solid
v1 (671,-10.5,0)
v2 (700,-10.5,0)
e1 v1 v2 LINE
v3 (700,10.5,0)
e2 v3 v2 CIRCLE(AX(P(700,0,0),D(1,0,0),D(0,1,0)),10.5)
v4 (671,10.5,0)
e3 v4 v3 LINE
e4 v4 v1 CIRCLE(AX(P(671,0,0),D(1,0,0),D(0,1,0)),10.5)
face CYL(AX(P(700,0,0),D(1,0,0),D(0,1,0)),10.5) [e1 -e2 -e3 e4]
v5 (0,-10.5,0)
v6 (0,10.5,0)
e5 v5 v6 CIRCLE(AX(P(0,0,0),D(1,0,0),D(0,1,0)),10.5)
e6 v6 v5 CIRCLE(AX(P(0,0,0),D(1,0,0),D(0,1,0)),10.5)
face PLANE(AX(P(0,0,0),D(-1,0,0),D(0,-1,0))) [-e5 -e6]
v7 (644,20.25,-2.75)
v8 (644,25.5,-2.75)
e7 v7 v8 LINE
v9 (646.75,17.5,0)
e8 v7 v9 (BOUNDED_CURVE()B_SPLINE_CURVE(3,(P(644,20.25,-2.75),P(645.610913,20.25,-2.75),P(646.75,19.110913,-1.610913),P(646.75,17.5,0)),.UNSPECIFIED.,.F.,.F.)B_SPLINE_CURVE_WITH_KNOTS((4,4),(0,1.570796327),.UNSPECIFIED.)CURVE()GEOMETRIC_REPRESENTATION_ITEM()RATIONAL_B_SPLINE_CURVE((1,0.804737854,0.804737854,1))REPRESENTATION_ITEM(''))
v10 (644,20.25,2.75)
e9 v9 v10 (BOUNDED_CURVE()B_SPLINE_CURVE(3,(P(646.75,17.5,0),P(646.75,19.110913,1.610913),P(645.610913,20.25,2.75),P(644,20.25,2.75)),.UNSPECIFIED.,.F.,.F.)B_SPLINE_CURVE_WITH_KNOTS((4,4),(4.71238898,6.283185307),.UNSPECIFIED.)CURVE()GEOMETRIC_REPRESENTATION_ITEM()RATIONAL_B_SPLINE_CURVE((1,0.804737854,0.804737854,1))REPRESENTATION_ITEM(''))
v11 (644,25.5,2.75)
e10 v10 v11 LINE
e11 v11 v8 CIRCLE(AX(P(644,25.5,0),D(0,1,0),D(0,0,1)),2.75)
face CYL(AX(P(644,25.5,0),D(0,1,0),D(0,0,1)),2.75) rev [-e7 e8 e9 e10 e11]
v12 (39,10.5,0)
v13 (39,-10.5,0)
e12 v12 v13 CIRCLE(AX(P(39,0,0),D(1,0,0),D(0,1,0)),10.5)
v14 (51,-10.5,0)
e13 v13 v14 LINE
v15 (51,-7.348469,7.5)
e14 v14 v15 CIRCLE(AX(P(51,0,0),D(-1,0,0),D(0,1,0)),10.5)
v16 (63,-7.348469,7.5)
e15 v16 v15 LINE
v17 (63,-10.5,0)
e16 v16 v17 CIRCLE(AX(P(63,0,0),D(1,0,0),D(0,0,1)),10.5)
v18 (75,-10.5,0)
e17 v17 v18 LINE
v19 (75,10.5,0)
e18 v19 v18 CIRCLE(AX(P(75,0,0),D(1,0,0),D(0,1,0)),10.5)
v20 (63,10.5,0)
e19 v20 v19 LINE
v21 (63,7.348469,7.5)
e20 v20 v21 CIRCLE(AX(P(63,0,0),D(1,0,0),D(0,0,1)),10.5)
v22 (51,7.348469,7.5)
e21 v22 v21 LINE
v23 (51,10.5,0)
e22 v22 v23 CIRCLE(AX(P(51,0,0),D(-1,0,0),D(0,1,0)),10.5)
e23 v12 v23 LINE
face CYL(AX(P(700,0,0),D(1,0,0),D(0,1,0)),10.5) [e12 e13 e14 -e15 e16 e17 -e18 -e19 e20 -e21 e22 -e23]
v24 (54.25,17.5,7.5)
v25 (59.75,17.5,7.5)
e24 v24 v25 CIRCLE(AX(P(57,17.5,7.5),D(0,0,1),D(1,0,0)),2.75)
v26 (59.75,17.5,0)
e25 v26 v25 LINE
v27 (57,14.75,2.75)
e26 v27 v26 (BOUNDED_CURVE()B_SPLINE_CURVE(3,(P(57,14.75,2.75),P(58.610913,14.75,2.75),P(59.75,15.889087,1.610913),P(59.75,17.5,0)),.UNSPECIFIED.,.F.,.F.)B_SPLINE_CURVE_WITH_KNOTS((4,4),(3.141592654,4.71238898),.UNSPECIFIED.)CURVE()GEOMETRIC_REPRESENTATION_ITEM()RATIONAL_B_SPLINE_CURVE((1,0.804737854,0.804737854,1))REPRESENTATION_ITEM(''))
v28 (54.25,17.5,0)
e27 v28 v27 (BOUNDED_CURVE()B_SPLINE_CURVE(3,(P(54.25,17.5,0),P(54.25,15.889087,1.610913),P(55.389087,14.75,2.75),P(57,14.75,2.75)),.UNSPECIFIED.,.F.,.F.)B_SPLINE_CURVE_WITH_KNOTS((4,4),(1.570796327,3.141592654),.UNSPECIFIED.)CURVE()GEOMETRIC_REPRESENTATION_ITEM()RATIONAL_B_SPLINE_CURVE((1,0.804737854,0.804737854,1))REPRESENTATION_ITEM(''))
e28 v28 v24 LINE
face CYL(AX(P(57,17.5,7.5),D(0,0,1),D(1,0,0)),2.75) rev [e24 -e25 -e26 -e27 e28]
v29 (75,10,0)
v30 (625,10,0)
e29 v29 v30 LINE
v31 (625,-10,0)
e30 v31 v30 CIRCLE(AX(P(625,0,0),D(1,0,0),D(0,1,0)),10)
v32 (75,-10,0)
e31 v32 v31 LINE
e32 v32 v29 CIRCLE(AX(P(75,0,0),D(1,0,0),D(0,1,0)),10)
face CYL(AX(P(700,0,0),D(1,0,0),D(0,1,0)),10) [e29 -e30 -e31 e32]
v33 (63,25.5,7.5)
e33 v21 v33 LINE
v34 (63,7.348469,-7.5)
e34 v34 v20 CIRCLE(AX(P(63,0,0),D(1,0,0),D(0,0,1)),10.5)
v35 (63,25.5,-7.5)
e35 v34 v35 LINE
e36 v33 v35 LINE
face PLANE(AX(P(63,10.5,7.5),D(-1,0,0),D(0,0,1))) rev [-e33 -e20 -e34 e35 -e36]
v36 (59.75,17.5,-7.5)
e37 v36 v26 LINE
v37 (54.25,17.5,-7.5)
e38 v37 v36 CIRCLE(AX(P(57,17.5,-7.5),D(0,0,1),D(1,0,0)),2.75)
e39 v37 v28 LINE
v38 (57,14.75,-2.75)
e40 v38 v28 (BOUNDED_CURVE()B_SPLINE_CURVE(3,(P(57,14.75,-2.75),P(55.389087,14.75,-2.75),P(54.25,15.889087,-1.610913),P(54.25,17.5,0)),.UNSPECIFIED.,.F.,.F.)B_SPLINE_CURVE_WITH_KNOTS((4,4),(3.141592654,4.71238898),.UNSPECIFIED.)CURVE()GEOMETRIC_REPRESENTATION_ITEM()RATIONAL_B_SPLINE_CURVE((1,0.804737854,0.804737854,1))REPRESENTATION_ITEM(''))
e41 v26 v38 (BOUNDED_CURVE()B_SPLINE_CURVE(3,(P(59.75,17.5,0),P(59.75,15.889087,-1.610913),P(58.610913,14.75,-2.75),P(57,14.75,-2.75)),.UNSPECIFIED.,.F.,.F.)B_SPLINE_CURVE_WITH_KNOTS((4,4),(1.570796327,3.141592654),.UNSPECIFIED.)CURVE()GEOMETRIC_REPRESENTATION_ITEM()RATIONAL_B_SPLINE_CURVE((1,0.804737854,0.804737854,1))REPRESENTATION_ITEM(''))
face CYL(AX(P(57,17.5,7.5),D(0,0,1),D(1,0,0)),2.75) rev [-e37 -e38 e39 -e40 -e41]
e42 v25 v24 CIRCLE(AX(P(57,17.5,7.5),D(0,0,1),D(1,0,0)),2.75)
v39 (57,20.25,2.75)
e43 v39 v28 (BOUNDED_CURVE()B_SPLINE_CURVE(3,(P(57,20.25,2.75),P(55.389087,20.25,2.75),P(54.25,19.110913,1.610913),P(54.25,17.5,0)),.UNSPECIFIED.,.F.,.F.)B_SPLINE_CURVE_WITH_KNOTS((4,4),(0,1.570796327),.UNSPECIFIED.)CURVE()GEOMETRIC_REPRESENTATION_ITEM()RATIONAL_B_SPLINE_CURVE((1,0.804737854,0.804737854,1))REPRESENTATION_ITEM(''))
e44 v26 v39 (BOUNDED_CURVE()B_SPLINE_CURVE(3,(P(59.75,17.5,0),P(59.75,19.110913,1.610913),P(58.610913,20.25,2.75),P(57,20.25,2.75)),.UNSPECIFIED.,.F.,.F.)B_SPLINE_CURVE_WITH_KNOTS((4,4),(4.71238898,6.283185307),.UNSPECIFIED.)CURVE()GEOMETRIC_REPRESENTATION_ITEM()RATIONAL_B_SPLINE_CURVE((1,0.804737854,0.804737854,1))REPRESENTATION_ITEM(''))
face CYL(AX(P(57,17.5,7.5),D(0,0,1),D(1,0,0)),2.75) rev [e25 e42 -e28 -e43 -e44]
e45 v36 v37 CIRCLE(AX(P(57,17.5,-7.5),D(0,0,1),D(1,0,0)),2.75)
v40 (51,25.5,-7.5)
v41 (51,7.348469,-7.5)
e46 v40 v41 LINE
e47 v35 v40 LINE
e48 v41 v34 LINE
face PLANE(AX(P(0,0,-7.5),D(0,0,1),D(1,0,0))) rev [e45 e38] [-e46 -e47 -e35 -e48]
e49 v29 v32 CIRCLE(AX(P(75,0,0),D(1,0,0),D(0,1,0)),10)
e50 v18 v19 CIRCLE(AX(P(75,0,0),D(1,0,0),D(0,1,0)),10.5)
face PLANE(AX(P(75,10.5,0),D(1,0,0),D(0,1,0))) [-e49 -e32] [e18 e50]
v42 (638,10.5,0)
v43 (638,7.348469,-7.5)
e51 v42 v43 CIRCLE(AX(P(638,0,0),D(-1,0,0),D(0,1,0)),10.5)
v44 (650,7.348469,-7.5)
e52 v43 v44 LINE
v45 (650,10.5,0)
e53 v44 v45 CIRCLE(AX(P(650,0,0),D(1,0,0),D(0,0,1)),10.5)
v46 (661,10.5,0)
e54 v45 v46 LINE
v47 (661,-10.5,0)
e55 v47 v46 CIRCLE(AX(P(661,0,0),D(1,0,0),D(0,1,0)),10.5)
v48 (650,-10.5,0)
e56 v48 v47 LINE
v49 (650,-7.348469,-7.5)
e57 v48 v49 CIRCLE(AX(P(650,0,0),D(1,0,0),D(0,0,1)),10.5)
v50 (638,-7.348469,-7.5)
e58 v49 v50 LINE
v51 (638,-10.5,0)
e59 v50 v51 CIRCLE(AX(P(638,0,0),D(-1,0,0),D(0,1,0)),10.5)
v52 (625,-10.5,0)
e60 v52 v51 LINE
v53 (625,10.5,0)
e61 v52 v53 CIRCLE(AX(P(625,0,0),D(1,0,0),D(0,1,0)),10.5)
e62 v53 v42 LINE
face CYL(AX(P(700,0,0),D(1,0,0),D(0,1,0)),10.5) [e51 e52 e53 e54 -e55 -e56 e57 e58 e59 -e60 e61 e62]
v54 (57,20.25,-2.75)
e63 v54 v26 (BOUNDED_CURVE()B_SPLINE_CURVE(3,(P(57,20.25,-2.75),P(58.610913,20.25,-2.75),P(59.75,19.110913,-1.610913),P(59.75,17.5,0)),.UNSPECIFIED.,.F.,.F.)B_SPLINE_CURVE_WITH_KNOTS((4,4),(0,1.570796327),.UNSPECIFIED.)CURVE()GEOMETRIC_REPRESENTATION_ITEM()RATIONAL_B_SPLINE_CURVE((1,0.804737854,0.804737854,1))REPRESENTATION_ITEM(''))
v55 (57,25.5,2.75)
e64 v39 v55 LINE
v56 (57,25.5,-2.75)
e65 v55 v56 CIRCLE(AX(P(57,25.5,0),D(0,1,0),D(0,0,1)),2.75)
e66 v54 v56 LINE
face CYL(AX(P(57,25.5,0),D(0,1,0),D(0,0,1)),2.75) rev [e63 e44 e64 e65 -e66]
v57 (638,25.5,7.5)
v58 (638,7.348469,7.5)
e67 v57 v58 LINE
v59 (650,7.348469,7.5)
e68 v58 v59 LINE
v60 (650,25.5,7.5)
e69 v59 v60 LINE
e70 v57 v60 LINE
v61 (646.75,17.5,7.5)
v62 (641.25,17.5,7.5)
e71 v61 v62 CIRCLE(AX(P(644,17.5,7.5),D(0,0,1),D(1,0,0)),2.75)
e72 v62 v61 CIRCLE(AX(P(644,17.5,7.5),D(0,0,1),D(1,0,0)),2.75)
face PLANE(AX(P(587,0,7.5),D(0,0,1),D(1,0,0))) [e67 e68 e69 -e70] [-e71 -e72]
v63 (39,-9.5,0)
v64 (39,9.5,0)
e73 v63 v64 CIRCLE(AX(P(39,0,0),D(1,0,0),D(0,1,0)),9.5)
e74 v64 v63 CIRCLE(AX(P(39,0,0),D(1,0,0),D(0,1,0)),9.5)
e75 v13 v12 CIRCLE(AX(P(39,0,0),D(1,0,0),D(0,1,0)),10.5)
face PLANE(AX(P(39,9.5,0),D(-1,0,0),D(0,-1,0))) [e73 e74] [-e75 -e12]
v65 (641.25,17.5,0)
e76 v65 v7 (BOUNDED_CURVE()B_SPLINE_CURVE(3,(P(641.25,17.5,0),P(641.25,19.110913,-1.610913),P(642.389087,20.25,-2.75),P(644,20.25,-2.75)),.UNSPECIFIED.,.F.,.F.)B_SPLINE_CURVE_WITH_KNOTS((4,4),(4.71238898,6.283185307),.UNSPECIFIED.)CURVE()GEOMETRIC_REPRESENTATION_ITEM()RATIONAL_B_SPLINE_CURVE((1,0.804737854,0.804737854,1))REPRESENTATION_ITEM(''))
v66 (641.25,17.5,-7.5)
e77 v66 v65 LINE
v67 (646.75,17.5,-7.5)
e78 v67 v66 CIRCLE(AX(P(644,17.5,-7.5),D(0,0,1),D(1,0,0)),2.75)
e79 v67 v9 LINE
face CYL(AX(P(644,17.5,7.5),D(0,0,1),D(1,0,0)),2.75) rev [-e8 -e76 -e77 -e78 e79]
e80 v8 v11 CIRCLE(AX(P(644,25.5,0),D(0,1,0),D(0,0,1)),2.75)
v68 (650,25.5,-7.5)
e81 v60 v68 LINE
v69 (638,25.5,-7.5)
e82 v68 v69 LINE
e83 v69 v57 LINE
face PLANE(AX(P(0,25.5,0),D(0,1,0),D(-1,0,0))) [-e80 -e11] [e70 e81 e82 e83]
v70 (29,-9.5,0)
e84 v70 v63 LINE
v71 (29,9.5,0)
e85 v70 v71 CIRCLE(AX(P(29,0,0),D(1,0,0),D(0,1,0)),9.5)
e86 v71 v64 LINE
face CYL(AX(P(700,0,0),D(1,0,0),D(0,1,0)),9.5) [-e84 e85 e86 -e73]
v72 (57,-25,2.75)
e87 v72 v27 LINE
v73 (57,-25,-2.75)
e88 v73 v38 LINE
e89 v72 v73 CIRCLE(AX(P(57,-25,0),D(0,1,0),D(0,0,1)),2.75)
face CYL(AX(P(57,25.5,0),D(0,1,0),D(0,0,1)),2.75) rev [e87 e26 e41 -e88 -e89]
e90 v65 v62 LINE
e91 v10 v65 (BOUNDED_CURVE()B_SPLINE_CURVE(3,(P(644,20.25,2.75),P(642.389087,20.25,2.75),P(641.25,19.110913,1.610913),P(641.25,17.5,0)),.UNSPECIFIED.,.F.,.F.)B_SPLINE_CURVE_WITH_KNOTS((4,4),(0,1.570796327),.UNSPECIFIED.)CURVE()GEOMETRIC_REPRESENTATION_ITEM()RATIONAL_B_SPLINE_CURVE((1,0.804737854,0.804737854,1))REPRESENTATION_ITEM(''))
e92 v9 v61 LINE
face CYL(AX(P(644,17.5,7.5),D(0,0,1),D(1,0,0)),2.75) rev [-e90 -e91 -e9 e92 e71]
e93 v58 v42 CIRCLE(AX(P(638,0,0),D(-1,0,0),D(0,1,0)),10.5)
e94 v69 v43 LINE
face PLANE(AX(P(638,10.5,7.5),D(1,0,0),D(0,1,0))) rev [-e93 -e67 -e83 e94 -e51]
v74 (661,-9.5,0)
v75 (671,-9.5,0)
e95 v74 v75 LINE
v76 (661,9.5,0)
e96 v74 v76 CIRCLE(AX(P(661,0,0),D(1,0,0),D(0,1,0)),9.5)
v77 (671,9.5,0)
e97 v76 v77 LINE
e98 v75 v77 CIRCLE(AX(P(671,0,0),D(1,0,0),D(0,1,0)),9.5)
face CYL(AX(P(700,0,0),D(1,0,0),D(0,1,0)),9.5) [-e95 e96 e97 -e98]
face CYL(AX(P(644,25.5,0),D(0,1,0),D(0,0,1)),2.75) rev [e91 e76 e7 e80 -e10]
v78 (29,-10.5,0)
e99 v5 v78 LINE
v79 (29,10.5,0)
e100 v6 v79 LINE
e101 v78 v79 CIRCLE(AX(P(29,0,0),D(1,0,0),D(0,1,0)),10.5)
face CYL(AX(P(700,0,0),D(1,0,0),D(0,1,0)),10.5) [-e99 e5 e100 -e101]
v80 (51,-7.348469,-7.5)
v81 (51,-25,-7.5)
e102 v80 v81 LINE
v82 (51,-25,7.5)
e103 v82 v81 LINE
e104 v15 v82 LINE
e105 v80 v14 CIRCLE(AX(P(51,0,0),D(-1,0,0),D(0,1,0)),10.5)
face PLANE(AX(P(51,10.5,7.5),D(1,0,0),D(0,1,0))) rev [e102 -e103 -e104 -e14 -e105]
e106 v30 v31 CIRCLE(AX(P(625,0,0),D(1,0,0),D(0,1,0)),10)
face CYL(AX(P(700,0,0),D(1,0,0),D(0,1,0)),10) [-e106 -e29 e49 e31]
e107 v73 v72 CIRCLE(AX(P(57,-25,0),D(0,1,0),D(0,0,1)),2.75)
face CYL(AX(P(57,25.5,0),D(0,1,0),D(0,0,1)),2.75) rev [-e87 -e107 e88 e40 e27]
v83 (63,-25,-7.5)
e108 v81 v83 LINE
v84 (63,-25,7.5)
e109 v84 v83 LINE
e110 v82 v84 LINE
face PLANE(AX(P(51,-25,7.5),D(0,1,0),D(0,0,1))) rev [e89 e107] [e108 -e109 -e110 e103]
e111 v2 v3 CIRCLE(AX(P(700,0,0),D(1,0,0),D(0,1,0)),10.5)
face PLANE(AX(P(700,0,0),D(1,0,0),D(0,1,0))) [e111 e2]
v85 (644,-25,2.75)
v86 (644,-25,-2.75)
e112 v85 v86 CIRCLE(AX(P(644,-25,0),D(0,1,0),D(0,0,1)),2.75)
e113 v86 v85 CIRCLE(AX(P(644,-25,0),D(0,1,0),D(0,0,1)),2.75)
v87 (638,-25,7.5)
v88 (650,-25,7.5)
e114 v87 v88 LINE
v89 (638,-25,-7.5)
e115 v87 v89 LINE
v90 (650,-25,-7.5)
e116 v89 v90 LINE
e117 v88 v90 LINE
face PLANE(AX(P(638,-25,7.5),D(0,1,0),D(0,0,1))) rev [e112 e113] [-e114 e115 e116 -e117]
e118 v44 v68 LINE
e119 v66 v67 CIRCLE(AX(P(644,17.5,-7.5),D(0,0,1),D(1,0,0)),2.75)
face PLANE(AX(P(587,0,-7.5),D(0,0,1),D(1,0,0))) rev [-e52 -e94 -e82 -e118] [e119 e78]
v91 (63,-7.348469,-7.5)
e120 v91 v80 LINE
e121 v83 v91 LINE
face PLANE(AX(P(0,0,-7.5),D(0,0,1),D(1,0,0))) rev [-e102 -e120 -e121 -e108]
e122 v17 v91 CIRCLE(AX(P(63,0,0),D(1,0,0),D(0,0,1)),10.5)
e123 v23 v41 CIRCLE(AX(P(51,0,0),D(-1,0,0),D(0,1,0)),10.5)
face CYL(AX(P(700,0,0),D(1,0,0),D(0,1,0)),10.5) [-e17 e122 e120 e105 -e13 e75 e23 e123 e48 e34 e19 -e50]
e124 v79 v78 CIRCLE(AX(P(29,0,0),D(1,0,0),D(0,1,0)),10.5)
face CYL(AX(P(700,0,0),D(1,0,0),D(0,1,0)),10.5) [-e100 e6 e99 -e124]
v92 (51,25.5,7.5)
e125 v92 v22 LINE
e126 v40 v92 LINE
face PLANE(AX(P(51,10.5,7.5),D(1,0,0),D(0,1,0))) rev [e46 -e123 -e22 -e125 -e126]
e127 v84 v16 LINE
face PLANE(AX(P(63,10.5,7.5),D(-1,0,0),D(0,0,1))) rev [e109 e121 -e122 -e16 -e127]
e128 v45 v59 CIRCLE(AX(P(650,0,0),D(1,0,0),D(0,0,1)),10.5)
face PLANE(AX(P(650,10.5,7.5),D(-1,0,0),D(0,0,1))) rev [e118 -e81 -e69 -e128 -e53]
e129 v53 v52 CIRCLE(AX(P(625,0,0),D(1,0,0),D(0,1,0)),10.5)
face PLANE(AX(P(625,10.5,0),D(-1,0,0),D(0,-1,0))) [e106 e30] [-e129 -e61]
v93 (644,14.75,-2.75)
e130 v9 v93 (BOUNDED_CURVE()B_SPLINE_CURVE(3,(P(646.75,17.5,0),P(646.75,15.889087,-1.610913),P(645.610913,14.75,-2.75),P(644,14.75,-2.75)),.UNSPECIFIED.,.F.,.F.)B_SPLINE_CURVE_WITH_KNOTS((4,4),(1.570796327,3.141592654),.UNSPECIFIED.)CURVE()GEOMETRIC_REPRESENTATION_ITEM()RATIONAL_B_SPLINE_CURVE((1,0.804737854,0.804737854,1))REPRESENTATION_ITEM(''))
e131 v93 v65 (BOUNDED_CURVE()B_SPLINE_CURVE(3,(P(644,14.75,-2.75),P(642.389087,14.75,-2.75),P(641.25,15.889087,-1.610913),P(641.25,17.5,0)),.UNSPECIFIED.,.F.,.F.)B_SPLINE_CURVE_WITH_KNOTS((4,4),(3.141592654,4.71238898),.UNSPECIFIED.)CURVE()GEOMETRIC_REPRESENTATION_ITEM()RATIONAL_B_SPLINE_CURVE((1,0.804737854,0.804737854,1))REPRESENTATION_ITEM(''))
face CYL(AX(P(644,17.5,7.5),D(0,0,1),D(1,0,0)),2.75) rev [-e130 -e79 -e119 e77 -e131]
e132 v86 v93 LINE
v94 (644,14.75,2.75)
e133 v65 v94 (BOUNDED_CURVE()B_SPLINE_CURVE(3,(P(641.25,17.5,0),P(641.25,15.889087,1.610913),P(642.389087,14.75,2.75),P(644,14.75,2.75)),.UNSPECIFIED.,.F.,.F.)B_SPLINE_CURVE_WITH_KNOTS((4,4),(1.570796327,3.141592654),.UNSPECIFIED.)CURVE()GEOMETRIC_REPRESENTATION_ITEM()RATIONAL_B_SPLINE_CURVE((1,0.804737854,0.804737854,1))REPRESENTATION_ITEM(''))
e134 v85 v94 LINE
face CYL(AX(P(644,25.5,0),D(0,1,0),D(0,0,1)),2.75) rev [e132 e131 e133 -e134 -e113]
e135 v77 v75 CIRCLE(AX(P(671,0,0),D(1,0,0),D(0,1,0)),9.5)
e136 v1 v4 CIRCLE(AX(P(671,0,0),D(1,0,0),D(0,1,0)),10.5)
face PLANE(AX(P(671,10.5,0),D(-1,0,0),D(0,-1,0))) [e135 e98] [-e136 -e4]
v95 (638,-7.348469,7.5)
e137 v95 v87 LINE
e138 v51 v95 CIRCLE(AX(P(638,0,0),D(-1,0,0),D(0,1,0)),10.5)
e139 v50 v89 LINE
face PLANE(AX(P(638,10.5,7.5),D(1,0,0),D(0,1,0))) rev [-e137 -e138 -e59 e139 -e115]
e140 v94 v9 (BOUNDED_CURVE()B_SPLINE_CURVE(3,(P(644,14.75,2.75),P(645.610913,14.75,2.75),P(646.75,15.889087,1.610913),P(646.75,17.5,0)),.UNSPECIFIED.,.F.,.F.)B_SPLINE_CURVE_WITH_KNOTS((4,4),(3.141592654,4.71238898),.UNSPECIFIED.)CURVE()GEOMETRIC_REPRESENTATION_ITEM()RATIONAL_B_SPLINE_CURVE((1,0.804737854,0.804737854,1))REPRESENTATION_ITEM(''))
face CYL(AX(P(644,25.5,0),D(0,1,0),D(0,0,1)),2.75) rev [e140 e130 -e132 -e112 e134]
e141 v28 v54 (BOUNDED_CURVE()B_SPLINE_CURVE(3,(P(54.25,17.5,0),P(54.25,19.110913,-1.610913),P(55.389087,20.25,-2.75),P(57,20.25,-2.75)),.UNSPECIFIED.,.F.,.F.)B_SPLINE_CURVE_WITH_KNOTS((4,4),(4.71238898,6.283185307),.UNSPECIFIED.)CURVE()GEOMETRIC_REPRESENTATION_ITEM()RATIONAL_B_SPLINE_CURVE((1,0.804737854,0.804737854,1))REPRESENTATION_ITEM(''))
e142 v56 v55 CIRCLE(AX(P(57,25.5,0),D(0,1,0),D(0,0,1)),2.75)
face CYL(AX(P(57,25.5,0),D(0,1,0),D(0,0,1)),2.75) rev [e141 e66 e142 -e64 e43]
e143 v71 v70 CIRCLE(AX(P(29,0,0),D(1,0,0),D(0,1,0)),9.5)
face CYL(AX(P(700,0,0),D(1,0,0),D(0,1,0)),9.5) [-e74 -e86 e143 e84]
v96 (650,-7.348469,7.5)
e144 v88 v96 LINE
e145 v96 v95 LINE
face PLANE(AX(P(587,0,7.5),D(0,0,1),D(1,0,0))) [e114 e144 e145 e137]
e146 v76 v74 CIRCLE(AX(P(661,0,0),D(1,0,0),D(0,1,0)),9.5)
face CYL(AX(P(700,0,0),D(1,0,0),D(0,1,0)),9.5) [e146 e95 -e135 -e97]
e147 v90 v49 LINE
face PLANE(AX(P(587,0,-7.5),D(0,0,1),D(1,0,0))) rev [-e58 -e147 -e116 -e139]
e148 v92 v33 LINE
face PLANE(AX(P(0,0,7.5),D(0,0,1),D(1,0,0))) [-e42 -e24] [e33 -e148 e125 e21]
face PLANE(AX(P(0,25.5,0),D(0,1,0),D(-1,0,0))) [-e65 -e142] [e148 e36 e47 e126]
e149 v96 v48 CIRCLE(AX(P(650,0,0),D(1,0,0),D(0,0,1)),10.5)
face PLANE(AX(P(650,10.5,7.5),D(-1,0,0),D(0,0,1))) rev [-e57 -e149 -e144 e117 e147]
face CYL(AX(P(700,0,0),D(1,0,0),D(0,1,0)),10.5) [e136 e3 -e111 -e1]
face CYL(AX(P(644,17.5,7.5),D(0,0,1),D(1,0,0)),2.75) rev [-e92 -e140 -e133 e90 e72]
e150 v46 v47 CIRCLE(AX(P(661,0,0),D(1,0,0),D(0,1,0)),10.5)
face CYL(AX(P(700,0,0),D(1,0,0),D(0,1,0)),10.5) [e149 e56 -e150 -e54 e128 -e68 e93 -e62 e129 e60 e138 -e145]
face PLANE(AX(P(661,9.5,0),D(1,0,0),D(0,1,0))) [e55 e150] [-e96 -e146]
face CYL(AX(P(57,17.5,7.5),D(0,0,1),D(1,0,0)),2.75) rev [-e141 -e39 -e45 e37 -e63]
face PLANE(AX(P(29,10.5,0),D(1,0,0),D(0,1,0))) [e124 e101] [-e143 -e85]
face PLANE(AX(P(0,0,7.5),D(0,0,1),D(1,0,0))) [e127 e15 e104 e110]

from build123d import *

# Parameters (mm, degrees)
SKETCH2_W            = 12
SKETCH2_H            = 35.5
BOSS_EXTRUDE1_DEPTH  = 7.5
LPATTERN1_COUNT      = 2
LPATTERN1_PITCH      = 587
BOSS_EXTRUDE2_DEPTH  = 15
M5_CLEARANCE_HOLE1_D = 5.5
M5_CLEARANCE_HOLE2_D = 5.5


with BuildPart() as part:
    # Sketch1 → Revolve1 (revolve)
    with BuildSketch(Plane.XY):
        Polygon((0, 0), (0, 10.5), (29, 10.5), (29, 9.5), (39, 9.5), (39, 10.5), (75, 10.5), (75, 10), (625, 10), (625, 10.5), (661, 10.5), (661, 9.5), (671, 9.5), (671, 10.5), (700, 10.5), (700, 0), align=None)
    revolve(axis=Axis((700, 0, 0), (-1, 0, 0)))

    # Sketch2 → Boss-Extrude1 (add, symmetric)
    with BuildSketch(Plane.XY):
        with Locations((57, -7.25)):
            Rectangle(SKETCH2_W, SKETCH2_H)
    boss_extrude1 = extrude(amount=BOSS_EXTRUDE1_DEPTH, both=True)

    # LPattern1: Boss-Extrude1 ×2
    with Locations(*[(i * LPATTERN1_PITCH, 0, 0) for i in range(1, LPATTERN1_COUNT)]):
        add(boss_extrude1)

    # Sketch3 → Boss-Extrude2 (add)
    with BuildSketch(Plane(origin=(0, 10.5, 0), x_dir=(1, 0, 0), z_dir=(0, 1, 0))):
        Polygon((63, -7.5), (63, 0), (63, 7.5), (51, 7.5), (51, 0), (51, -7.5), align=None)
        Polygon((650, -7.5), (650, 0), (650, 7.5), (638, 7.5), (638, 0), (638, -7.5), align=None)
    extrude(amount=BOSS_EXTRUDE2_DEPTH)

    # M5 Clearance Hole1 (through all)
    with Locations(Plane(origin=(0, 25.5, 0), x_dir=(1, 0, 0), z_dir=(0, 1, 0))):
        with Locations((57, 0), (644, 0)):
            Hole(M5_CLEARANCE_HOLE1_D / 2)

    # M5 Clearance Hole2 (through all)
    with Locations(Plane.XY.offset(7.5)):
        with Locations((57, 17.5), (644, 17.5)):
            Hole(M5_CLEARANCE_HOLE2_D / 2)


solid = part.part
